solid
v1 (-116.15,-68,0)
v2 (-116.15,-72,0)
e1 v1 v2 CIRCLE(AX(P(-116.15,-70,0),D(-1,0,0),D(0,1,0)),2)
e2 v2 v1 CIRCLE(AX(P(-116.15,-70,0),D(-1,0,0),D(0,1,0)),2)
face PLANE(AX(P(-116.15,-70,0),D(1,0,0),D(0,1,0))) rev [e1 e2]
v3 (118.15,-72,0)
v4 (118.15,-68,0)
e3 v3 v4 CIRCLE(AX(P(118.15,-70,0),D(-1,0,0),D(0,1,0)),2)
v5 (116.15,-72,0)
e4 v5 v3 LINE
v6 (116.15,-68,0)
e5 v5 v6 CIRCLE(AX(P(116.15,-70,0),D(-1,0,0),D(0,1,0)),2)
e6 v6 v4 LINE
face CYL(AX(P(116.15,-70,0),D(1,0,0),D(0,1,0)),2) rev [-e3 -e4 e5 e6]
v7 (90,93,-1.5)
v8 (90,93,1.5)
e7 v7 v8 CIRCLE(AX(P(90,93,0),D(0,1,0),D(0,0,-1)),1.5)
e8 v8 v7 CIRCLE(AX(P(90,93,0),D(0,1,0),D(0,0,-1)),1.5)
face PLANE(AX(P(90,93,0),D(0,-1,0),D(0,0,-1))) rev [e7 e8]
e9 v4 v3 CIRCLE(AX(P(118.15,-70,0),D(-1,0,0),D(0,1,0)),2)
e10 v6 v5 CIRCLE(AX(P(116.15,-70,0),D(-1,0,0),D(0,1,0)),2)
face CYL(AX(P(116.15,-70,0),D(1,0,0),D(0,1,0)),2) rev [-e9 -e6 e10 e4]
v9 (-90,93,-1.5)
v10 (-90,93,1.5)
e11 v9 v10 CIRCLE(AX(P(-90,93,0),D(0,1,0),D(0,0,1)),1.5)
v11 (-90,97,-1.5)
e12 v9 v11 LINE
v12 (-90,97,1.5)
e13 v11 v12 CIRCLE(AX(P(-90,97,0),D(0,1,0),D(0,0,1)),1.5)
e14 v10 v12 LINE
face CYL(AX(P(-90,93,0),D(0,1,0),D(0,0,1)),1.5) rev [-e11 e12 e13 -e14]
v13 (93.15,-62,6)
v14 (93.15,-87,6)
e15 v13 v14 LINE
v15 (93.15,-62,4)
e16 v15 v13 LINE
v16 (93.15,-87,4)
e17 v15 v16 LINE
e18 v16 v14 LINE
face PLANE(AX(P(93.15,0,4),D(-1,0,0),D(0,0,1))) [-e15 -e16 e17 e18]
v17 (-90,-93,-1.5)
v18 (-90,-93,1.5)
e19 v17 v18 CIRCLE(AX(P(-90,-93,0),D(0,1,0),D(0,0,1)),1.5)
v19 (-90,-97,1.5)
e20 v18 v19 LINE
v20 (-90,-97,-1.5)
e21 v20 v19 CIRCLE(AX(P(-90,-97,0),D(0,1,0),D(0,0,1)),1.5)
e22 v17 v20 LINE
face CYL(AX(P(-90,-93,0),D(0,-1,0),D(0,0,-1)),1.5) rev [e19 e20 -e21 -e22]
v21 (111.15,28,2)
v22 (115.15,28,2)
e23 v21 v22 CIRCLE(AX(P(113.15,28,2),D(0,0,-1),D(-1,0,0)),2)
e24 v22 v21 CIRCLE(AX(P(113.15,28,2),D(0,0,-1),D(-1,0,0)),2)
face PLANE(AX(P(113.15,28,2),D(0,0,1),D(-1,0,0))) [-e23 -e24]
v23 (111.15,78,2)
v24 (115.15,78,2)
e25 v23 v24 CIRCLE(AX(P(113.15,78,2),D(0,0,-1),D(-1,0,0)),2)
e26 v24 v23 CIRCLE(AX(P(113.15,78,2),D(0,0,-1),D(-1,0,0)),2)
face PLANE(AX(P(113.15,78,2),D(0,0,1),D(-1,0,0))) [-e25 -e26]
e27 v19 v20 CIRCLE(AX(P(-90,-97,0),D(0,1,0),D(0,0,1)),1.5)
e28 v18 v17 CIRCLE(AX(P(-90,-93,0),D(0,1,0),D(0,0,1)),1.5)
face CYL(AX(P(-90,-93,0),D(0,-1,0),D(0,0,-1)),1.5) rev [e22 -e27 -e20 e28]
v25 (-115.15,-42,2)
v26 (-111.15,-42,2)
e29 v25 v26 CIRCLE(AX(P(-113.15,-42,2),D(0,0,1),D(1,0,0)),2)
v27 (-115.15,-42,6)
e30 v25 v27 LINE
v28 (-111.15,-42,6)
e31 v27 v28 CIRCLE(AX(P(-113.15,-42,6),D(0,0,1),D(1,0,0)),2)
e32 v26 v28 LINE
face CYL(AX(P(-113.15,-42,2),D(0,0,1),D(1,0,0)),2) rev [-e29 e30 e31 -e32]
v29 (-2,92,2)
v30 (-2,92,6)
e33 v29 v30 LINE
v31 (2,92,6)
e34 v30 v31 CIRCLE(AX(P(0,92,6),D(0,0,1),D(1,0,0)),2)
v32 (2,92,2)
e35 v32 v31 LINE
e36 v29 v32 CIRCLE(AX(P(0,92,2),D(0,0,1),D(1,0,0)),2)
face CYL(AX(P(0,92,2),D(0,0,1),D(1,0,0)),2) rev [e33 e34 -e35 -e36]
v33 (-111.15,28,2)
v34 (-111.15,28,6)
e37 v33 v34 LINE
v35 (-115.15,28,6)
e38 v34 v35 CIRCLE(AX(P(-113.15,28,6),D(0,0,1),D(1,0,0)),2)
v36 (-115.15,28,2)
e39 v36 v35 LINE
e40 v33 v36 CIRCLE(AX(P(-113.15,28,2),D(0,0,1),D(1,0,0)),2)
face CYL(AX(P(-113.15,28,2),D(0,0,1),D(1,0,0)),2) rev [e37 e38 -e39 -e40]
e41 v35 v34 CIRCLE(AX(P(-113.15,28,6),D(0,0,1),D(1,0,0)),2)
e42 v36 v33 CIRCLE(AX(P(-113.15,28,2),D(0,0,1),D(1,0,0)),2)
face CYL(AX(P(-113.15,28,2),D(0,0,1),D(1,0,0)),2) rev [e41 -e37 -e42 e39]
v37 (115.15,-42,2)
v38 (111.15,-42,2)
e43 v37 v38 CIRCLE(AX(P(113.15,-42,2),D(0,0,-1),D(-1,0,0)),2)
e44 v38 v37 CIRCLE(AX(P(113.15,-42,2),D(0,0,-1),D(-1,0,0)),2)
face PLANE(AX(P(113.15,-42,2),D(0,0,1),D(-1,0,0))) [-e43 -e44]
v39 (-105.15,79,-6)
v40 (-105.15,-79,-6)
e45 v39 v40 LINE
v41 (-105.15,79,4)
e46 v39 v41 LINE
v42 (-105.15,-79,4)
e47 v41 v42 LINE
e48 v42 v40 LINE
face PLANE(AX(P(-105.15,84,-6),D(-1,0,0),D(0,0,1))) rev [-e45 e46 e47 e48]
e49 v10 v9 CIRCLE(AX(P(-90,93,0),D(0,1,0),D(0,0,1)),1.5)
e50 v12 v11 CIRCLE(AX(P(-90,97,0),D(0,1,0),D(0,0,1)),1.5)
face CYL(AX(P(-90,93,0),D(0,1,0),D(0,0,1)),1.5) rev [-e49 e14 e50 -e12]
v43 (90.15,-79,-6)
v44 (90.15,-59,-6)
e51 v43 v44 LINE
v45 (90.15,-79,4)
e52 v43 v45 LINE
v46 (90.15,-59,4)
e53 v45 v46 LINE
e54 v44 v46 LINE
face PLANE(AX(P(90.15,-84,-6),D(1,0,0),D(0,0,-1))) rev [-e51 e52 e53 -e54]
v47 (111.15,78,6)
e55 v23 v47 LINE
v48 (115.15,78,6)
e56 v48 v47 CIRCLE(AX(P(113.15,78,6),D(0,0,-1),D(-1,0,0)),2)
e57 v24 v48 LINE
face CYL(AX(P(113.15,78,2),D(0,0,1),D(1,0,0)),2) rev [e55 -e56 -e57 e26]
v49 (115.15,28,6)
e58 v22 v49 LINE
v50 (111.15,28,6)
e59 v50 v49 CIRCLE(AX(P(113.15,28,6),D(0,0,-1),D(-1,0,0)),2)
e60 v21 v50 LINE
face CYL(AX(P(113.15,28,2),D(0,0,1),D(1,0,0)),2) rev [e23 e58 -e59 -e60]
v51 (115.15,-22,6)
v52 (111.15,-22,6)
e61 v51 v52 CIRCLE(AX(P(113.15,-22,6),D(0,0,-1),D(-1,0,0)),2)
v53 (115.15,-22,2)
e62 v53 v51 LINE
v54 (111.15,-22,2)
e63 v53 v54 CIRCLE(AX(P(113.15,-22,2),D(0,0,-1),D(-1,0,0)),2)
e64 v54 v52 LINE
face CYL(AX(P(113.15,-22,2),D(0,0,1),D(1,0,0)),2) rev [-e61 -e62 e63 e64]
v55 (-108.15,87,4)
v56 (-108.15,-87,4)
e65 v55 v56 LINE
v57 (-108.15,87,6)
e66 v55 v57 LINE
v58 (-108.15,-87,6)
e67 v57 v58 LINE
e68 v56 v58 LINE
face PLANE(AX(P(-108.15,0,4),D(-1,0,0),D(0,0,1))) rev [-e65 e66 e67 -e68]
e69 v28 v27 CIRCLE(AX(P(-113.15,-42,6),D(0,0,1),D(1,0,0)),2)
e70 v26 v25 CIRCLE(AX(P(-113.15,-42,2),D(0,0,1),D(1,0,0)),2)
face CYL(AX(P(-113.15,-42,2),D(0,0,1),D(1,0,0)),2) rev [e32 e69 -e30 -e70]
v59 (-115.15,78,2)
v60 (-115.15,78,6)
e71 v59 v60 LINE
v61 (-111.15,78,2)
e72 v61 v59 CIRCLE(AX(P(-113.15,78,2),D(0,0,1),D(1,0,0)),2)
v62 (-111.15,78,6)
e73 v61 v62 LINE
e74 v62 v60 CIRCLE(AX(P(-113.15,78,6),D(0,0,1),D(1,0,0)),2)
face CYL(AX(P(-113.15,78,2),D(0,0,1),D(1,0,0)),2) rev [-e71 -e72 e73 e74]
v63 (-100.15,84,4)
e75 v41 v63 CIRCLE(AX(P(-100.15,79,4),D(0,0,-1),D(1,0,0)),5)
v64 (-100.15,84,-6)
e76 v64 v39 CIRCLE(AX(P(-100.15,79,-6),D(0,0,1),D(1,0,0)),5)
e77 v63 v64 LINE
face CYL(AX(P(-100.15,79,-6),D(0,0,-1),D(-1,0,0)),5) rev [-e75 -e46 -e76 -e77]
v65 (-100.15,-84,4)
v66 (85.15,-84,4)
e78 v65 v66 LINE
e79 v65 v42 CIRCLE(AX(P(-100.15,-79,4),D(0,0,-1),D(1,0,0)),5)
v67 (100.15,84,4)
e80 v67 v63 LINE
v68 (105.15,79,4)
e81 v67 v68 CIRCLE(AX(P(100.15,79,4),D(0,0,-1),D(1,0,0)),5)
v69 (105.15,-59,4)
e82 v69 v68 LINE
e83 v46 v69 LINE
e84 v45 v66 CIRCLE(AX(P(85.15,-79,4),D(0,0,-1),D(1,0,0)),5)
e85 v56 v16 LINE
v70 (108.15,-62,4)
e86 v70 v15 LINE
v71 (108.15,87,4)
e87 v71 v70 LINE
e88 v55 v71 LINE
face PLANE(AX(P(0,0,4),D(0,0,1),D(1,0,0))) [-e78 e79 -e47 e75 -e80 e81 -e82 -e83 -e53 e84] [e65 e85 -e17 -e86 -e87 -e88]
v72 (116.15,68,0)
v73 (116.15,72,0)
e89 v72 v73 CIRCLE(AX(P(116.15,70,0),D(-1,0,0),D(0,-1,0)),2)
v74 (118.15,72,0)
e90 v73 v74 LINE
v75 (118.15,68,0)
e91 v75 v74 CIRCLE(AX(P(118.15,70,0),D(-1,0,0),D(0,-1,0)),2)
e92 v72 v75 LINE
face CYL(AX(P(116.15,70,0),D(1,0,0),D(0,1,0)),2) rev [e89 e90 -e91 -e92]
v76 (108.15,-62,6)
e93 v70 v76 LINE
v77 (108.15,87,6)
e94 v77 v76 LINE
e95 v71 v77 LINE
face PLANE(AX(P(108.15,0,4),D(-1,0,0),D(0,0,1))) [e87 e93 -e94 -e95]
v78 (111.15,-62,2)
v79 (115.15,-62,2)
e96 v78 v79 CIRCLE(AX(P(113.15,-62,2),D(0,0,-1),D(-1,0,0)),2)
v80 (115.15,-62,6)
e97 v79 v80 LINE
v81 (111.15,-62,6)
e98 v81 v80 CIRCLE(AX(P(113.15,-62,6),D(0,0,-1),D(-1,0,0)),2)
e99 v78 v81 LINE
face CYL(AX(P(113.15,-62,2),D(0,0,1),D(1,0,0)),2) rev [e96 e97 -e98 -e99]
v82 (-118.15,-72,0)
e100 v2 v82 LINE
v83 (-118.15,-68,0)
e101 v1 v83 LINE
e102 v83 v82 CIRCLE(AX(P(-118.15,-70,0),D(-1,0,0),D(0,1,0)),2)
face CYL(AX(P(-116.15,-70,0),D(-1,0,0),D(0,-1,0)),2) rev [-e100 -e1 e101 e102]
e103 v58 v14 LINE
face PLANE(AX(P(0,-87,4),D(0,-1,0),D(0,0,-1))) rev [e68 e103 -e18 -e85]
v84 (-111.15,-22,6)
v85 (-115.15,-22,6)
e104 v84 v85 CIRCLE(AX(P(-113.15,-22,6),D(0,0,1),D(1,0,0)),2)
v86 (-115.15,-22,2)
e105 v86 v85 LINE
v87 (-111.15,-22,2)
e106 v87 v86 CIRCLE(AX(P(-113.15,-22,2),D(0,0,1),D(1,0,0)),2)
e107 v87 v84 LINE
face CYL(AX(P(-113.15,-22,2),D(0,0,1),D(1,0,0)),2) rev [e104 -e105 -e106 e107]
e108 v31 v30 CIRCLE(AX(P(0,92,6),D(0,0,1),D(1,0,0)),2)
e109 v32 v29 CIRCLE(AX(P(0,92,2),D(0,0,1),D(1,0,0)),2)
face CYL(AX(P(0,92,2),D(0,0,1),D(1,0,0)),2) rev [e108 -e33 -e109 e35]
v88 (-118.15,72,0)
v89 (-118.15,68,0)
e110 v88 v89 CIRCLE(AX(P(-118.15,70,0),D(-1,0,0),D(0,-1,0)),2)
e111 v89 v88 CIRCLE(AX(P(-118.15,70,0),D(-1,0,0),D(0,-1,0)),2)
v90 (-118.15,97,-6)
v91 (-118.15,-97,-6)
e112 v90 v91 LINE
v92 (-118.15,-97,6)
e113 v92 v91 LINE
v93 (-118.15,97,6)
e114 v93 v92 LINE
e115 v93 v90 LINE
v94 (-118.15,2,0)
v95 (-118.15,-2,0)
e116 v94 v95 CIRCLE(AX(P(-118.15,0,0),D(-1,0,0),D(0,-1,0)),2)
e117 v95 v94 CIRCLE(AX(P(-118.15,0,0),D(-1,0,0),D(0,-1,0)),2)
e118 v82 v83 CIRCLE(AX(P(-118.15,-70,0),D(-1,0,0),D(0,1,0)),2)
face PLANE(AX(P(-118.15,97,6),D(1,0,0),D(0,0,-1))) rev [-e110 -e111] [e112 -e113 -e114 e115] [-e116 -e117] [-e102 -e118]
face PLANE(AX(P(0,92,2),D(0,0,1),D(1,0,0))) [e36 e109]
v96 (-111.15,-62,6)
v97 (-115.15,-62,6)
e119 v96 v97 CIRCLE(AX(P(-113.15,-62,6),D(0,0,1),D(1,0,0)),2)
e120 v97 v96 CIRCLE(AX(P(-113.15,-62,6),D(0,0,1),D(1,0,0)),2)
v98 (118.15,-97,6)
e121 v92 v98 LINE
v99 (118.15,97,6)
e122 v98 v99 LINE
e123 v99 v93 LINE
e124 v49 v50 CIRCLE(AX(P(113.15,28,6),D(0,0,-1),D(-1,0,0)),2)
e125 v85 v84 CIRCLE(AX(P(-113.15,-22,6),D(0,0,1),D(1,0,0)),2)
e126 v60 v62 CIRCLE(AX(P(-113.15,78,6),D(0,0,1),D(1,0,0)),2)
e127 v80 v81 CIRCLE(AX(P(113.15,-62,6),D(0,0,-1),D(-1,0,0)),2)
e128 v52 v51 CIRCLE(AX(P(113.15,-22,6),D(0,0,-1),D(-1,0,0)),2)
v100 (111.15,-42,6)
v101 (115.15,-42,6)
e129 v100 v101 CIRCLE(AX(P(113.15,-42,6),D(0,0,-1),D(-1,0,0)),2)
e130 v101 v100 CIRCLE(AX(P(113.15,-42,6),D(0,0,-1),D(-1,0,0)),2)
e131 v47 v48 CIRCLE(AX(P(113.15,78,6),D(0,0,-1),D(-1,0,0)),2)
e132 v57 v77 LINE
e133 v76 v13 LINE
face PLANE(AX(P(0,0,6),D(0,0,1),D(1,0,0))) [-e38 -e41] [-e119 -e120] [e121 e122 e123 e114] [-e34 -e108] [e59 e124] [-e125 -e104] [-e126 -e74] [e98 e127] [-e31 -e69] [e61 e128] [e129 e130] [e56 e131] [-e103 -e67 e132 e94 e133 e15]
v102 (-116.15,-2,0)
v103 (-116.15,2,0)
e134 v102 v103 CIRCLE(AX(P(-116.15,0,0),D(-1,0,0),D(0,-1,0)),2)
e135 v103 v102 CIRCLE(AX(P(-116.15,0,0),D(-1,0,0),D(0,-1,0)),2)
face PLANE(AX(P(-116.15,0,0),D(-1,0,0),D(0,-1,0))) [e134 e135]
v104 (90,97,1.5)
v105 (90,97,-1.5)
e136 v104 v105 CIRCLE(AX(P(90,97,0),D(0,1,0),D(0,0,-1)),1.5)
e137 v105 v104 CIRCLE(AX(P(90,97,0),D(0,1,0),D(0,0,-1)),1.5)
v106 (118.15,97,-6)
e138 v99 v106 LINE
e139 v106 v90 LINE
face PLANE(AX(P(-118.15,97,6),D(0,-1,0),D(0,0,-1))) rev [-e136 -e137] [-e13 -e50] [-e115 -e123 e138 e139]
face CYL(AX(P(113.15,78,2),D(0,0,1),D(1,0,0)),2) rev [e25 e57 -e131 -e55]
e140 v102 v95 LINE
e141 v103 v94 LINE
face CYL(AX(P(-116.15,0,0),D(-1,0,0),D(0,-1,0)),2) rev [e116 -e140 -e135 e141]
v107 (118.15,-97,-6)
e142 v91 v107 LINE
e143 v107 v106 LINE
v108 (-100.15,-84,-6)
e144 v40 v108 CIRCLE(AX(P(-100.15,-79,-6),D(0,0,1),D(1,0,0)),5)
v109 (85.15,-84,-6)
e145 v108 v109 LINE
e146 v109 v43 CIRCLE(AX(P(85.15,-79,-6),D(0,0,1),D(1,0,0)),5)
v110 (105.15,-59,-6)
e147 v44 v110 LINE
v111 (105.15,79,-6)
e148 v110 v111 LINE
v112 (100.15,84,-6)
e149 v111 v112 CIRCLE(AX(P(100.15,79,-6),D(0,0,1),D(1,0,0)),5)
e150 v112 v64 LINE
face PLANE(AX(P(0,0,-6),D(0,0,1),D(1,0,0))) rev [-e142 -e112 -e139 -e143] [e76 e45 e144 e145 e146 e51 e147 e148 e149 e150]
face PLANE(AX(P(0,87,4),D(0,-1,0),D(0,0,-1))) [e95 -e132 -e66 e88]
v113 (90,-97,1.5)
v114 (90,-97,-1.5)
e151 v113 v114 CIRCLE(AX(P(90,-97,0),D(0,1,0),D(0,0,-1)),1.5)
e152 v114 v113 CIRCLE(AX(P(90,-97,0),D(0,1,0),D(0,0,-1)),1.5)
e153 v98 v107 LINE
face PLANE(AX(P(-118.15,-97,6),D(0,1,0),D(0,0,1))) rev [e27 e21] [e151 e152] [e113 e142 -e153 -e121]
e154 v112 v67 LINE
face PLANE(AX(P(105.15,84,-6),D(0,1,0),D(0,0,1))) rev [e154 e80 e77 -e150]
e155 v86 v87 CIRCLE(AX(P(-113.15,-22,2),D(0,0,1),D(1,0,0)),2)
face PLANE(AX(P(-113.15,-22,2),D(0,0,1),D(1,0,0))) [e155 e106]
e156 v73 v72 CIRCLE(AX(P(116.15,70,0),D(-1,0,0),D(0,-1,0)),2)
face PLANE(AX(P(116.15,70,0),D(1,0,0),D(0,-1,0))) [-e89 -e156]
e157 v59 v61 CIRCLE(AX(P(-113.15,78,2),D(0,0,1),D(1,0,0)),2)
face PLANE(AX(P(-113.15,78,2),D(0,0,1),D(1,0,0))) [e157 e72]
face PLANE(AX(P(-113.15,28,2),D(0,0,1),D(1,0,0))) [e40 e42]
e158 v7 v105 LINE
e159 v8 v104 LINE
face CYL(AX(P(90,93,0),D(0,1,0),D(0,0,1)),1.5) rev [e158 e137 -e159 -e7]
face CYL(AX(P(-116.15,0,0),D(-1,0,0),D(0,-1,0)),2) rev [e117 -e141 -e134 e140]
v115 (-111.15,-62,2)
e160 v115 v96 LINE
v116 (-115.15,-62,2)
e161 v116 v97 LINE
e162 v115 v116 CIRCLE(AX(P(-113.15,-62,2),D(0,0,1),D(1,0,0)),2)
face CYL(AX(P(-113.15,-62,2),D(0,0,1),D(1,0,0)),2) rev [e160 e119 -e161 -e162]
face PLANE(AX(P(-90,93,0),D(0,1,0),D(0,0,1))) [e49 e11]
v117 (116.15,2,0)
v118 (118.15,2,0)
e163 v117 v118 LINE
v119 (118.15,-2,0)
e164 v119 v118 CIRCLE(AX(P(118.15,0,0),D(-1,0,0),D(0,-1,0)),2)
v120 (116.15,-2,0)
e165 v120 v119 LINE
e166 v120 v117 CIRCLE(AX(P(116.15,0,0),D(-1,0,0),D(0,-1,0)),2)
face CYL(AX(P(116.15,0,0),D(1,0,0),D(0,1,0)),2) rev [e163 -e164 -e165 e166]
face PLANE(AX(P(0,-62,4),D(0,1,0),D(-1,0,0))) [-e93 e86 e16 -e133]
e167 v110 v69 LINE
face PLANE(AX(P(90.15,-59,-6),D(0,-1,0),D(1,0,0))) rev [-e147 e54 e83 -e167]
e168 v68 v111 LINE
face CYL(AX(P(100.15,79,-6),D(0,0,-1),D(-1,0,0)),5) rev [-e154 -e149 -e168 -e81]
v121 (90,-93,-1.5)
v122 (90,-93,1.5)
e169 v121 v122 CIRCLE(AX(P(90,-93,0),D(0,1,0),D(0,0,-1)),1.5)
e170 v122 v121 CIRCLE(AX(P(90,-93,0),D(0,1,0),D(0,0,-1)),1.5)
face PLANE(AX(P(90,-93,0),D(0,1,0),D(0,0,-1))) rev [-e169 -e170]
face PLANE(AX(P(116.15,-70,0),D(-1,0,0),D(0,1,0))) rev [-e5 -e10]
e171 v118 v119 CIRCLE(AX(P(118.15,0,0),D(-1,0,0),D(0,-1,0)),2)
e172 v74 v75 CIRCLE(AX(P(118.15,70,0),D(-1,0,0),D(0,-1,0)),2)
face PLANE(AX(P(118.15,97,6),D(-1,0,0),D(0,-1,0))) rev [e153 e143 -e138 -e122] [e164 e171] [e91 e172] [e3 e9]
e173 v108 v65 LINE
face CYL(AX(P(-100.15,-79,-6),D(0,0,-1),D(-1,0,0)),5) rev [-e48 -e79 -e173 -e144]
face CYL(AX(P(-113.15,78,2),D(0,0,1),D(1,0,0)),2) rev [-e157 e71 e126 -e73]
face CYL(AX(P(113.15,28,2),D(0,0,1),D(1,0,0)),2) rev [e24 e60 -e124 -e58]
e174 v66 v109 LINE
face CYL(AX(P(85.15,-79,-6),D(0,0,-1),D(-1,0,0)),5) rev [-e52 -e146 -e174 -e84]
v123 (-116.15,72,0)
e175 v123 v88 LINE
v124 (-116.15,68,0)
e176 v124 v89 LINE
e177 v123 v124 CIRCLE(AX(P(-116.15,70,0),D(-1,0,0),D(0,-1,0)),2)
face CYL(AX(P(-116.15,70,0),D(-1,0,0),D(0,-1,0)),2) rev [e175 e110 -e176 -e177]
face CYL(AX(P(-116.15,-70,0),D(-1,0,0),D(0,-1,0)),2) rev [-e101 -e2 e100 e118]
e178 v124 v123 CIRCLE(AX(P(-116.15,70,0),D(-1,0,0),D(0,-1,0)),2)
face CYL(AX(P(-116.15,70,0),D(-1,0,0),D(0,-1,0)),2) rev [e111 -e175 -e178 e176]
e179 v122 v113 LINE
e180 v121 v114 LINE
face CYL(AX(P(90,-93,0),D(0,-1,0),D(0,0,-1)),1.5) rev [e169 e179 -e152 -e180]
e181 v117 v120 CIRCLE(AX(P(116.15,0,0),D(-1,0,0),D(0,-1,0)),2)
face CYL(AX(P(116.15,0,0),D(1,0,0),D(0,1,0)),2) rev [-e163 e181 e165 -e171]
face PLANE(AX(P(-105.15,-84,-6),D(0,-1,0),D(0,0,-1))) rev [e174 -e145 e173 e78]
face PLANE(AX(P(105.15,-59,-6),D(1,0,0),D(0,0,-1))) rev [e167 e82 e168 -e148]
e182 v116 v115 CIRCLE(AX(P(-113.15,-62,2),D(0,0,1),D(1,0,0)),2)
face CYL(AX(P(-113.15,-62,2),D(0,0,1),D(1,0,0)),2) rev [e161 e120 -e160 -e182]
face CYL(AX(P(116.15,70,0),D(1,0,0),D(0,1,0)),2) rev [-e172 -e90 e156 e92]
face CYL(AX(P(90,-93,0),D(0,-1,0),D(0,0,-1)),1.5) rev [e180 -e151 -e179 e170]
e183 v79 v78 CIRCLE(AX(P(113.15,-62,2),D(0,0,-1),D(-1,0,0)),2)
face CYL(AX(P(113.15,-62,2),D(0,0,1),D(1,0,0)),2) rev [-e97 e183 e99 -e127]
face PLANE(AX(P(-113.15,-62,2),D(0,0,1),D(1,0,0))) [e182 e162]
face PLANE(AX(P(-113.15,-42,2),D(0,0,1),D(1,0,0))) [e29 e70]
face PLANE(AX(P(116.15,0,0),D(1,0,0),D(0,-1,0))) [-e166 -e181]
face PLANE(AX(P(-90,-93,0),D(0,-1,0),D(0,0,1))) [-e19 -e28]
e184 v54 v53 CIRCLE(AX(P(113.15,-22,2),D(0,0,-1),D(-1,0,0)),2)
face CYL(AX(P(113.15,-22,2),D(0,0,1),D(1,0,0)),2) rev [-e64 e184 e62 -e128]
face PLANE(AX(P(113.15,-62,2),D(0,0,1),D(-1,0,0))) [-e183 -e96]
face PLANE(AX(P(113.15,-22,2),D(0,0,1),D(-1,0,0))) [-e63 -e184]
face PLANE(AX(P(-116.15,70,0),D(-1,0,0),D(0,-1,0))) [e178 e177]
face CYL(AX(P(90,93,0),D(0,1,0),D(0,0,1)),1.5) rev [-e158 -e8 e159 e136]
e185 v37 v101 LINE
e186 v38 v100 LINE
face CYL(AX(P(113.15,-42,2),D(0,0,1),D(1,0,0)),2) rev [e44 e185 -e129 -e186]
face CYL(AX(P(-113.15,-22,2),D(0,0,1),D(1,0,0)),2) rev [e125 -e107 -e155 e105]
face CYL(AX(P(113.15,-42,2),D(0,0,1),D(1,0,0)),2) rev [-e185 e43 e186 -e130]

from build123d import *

# Parameters (mm, degrees)
SKETCH1_W           = 236.3
SKETCH1_H           = 194
BOSS_EXTRUDE1_DEPTH = 6
CUT_EXTRUDE1_DEPTH  = 2
CUT_EXTRUDE2_DEPTH  = 154.194068097
FILLET1_R           = 5
SKETCH4_R           = 2
CUT_EXTRUDE3_DEPTH  = 2
SKETCH5_R           = 1.5
CUT_EXTRUDE4_DEPTH  = 4
SKETCH7_R           = 2
CUT_EXTRUDE6_DEPTH  = 4
SKETCH8_R           = 2
CUT_EXTRUDE7_DEPTH  = 4


with BuildPart() as part:
    # Sketch1 → Boss-Extrude1 (new, symmetric)
    with BuildSketch(Plane.XY):
        Rectangle(SKETCH1_W, SKETCH1_H)
    extrude(amount=BOSS_EXTRUDE1_DEPTH, both=True)

    # Sketch2 → Cut-Extrude1 (cut)
    with BuildSketch(Plane.XY.offset(6)):
        Polygon((108.15, 87), (-108.15, 87), (-108.15, -87), (93.15, -87), (93.15, -62), (108.15, -62), align=None)
    extrude(amount=-CUT_EXTRUDE1_DEPTH, mode=Mode.SUBTRACT)

    # Sketch3 → Cut-Extrude2 (cut, through all)
    with BuildSketch(Plane.XY.offset(4)):
        Polygon((90.15, -84), (90.15, -59), (105.15, -59), (105.15, 84), (-105.15, 84), (-105.15, -84), align=None)
    extrude(amount=-CUT_EXTRUDE2_DEPTH, mode=Mode.SUBTRACT)

    # Fillet1
    fillet1_edges = [part.edges().sort_by_distance(p)[0] for p in [
        (90.15, -84, -1),
        (-105.15, -84, -1),
        (-105.15, 84, -1),
        (105.15, 84, -1),
    ]]
    fillet(fillet1_edges, radius=FILLET1_R)

    # Sketch4 → Cut-Extrude3 (cut)
    with BuildSketch(Plane.ZY.offset(118.15)):
        with Locations(Location((0, 0, 0), (0, 0, 270))):
            Circle(SKETCH4_R)
        with Locations(Location((0, 70, 0), (0, 0, 270))):
            Circle(SKETCH4_R)
        with Locations(Location((0, -70, 0), (0, 0, 90))):
            Circle(SKETCH4_R)
    cut_extrude3 = extrude(amount=-CUT_EXTRUDE3_DEPTH, mode=Mode.SUBTRACT)

    # Mirror1: Cut-Extrude3 across plane
    add(cut_extrude3.mirror(Plane(origin=(0, 0, 0), x_dir=(0, 0, 1), z_dir=(1, 0, 0))), mode=Mode.SUBTRACT)

    # Sketch5 → Cut-Extrude4 (cut)
    with BuildSketch(Plane(origin=(0, 97, 0), x_dir=(1, 0, 0), z_dir=(0, 1, 0))):
        with Locations(Location((-90, 0, 0), (0, 0, 270))):
            Circle(SKETCH5_R)
        with Locations(Location((90, 0, 0), (0, 0, 90))):
            Circle(SKETCH5_R)
    cut_extrude4 = extrude(amount=-CUT_EXTRUDE4_DEPTH, mode=Mode.SUBTRACT)

    # Mirror2: Cut-Extrude4 across plane
    add(cut_extrude4.mirror(Plane.ZX), mode=Mode.SUBTRACT)

    # Sketch7 → Cut-Extrude6 (cut)
    with BuildSketch(Plane.XY.offset(6)):
        with Locations((-113.15, 78)):
            Circle(SKETCH7_R)
        with Locations((-113.15, 28)):
            Circle(SKETCH7_R)
        with Locations((-113.15, -22)):
            Circle(SKETCH7_R)
        with Locations((-113.15, -42)):
            Circle(SKETCH7_R)
        with Locations((-113.15, -62)):
            Circle(SKETCH7_R)
    cut_extrude6 = extrude(amount=-CUT_EXTRUDE6_DEPTH, mode=Mode.SUBTRACT)

    # Mirror3: Cut-Extrude6 across plane
    add(cut_extrude6.mirror(Plane(origin=(0, 0, 0), x_dir=(0, 0, 1), z_dir=(1, 0, 0))), mode=Mode.SUBTRACT)

    # Sketch8 → Cut-Extrude7 (cut)
    with BuildSketch(Plane.XY.offset(6)):
        with Locations((0, 92)):
            Circle(SKETCH8_R)
    extrude(amount=-CUT_EXTRUDE7_DEPTH, mode=Mode.SUBTRACT)


solid = part.part
